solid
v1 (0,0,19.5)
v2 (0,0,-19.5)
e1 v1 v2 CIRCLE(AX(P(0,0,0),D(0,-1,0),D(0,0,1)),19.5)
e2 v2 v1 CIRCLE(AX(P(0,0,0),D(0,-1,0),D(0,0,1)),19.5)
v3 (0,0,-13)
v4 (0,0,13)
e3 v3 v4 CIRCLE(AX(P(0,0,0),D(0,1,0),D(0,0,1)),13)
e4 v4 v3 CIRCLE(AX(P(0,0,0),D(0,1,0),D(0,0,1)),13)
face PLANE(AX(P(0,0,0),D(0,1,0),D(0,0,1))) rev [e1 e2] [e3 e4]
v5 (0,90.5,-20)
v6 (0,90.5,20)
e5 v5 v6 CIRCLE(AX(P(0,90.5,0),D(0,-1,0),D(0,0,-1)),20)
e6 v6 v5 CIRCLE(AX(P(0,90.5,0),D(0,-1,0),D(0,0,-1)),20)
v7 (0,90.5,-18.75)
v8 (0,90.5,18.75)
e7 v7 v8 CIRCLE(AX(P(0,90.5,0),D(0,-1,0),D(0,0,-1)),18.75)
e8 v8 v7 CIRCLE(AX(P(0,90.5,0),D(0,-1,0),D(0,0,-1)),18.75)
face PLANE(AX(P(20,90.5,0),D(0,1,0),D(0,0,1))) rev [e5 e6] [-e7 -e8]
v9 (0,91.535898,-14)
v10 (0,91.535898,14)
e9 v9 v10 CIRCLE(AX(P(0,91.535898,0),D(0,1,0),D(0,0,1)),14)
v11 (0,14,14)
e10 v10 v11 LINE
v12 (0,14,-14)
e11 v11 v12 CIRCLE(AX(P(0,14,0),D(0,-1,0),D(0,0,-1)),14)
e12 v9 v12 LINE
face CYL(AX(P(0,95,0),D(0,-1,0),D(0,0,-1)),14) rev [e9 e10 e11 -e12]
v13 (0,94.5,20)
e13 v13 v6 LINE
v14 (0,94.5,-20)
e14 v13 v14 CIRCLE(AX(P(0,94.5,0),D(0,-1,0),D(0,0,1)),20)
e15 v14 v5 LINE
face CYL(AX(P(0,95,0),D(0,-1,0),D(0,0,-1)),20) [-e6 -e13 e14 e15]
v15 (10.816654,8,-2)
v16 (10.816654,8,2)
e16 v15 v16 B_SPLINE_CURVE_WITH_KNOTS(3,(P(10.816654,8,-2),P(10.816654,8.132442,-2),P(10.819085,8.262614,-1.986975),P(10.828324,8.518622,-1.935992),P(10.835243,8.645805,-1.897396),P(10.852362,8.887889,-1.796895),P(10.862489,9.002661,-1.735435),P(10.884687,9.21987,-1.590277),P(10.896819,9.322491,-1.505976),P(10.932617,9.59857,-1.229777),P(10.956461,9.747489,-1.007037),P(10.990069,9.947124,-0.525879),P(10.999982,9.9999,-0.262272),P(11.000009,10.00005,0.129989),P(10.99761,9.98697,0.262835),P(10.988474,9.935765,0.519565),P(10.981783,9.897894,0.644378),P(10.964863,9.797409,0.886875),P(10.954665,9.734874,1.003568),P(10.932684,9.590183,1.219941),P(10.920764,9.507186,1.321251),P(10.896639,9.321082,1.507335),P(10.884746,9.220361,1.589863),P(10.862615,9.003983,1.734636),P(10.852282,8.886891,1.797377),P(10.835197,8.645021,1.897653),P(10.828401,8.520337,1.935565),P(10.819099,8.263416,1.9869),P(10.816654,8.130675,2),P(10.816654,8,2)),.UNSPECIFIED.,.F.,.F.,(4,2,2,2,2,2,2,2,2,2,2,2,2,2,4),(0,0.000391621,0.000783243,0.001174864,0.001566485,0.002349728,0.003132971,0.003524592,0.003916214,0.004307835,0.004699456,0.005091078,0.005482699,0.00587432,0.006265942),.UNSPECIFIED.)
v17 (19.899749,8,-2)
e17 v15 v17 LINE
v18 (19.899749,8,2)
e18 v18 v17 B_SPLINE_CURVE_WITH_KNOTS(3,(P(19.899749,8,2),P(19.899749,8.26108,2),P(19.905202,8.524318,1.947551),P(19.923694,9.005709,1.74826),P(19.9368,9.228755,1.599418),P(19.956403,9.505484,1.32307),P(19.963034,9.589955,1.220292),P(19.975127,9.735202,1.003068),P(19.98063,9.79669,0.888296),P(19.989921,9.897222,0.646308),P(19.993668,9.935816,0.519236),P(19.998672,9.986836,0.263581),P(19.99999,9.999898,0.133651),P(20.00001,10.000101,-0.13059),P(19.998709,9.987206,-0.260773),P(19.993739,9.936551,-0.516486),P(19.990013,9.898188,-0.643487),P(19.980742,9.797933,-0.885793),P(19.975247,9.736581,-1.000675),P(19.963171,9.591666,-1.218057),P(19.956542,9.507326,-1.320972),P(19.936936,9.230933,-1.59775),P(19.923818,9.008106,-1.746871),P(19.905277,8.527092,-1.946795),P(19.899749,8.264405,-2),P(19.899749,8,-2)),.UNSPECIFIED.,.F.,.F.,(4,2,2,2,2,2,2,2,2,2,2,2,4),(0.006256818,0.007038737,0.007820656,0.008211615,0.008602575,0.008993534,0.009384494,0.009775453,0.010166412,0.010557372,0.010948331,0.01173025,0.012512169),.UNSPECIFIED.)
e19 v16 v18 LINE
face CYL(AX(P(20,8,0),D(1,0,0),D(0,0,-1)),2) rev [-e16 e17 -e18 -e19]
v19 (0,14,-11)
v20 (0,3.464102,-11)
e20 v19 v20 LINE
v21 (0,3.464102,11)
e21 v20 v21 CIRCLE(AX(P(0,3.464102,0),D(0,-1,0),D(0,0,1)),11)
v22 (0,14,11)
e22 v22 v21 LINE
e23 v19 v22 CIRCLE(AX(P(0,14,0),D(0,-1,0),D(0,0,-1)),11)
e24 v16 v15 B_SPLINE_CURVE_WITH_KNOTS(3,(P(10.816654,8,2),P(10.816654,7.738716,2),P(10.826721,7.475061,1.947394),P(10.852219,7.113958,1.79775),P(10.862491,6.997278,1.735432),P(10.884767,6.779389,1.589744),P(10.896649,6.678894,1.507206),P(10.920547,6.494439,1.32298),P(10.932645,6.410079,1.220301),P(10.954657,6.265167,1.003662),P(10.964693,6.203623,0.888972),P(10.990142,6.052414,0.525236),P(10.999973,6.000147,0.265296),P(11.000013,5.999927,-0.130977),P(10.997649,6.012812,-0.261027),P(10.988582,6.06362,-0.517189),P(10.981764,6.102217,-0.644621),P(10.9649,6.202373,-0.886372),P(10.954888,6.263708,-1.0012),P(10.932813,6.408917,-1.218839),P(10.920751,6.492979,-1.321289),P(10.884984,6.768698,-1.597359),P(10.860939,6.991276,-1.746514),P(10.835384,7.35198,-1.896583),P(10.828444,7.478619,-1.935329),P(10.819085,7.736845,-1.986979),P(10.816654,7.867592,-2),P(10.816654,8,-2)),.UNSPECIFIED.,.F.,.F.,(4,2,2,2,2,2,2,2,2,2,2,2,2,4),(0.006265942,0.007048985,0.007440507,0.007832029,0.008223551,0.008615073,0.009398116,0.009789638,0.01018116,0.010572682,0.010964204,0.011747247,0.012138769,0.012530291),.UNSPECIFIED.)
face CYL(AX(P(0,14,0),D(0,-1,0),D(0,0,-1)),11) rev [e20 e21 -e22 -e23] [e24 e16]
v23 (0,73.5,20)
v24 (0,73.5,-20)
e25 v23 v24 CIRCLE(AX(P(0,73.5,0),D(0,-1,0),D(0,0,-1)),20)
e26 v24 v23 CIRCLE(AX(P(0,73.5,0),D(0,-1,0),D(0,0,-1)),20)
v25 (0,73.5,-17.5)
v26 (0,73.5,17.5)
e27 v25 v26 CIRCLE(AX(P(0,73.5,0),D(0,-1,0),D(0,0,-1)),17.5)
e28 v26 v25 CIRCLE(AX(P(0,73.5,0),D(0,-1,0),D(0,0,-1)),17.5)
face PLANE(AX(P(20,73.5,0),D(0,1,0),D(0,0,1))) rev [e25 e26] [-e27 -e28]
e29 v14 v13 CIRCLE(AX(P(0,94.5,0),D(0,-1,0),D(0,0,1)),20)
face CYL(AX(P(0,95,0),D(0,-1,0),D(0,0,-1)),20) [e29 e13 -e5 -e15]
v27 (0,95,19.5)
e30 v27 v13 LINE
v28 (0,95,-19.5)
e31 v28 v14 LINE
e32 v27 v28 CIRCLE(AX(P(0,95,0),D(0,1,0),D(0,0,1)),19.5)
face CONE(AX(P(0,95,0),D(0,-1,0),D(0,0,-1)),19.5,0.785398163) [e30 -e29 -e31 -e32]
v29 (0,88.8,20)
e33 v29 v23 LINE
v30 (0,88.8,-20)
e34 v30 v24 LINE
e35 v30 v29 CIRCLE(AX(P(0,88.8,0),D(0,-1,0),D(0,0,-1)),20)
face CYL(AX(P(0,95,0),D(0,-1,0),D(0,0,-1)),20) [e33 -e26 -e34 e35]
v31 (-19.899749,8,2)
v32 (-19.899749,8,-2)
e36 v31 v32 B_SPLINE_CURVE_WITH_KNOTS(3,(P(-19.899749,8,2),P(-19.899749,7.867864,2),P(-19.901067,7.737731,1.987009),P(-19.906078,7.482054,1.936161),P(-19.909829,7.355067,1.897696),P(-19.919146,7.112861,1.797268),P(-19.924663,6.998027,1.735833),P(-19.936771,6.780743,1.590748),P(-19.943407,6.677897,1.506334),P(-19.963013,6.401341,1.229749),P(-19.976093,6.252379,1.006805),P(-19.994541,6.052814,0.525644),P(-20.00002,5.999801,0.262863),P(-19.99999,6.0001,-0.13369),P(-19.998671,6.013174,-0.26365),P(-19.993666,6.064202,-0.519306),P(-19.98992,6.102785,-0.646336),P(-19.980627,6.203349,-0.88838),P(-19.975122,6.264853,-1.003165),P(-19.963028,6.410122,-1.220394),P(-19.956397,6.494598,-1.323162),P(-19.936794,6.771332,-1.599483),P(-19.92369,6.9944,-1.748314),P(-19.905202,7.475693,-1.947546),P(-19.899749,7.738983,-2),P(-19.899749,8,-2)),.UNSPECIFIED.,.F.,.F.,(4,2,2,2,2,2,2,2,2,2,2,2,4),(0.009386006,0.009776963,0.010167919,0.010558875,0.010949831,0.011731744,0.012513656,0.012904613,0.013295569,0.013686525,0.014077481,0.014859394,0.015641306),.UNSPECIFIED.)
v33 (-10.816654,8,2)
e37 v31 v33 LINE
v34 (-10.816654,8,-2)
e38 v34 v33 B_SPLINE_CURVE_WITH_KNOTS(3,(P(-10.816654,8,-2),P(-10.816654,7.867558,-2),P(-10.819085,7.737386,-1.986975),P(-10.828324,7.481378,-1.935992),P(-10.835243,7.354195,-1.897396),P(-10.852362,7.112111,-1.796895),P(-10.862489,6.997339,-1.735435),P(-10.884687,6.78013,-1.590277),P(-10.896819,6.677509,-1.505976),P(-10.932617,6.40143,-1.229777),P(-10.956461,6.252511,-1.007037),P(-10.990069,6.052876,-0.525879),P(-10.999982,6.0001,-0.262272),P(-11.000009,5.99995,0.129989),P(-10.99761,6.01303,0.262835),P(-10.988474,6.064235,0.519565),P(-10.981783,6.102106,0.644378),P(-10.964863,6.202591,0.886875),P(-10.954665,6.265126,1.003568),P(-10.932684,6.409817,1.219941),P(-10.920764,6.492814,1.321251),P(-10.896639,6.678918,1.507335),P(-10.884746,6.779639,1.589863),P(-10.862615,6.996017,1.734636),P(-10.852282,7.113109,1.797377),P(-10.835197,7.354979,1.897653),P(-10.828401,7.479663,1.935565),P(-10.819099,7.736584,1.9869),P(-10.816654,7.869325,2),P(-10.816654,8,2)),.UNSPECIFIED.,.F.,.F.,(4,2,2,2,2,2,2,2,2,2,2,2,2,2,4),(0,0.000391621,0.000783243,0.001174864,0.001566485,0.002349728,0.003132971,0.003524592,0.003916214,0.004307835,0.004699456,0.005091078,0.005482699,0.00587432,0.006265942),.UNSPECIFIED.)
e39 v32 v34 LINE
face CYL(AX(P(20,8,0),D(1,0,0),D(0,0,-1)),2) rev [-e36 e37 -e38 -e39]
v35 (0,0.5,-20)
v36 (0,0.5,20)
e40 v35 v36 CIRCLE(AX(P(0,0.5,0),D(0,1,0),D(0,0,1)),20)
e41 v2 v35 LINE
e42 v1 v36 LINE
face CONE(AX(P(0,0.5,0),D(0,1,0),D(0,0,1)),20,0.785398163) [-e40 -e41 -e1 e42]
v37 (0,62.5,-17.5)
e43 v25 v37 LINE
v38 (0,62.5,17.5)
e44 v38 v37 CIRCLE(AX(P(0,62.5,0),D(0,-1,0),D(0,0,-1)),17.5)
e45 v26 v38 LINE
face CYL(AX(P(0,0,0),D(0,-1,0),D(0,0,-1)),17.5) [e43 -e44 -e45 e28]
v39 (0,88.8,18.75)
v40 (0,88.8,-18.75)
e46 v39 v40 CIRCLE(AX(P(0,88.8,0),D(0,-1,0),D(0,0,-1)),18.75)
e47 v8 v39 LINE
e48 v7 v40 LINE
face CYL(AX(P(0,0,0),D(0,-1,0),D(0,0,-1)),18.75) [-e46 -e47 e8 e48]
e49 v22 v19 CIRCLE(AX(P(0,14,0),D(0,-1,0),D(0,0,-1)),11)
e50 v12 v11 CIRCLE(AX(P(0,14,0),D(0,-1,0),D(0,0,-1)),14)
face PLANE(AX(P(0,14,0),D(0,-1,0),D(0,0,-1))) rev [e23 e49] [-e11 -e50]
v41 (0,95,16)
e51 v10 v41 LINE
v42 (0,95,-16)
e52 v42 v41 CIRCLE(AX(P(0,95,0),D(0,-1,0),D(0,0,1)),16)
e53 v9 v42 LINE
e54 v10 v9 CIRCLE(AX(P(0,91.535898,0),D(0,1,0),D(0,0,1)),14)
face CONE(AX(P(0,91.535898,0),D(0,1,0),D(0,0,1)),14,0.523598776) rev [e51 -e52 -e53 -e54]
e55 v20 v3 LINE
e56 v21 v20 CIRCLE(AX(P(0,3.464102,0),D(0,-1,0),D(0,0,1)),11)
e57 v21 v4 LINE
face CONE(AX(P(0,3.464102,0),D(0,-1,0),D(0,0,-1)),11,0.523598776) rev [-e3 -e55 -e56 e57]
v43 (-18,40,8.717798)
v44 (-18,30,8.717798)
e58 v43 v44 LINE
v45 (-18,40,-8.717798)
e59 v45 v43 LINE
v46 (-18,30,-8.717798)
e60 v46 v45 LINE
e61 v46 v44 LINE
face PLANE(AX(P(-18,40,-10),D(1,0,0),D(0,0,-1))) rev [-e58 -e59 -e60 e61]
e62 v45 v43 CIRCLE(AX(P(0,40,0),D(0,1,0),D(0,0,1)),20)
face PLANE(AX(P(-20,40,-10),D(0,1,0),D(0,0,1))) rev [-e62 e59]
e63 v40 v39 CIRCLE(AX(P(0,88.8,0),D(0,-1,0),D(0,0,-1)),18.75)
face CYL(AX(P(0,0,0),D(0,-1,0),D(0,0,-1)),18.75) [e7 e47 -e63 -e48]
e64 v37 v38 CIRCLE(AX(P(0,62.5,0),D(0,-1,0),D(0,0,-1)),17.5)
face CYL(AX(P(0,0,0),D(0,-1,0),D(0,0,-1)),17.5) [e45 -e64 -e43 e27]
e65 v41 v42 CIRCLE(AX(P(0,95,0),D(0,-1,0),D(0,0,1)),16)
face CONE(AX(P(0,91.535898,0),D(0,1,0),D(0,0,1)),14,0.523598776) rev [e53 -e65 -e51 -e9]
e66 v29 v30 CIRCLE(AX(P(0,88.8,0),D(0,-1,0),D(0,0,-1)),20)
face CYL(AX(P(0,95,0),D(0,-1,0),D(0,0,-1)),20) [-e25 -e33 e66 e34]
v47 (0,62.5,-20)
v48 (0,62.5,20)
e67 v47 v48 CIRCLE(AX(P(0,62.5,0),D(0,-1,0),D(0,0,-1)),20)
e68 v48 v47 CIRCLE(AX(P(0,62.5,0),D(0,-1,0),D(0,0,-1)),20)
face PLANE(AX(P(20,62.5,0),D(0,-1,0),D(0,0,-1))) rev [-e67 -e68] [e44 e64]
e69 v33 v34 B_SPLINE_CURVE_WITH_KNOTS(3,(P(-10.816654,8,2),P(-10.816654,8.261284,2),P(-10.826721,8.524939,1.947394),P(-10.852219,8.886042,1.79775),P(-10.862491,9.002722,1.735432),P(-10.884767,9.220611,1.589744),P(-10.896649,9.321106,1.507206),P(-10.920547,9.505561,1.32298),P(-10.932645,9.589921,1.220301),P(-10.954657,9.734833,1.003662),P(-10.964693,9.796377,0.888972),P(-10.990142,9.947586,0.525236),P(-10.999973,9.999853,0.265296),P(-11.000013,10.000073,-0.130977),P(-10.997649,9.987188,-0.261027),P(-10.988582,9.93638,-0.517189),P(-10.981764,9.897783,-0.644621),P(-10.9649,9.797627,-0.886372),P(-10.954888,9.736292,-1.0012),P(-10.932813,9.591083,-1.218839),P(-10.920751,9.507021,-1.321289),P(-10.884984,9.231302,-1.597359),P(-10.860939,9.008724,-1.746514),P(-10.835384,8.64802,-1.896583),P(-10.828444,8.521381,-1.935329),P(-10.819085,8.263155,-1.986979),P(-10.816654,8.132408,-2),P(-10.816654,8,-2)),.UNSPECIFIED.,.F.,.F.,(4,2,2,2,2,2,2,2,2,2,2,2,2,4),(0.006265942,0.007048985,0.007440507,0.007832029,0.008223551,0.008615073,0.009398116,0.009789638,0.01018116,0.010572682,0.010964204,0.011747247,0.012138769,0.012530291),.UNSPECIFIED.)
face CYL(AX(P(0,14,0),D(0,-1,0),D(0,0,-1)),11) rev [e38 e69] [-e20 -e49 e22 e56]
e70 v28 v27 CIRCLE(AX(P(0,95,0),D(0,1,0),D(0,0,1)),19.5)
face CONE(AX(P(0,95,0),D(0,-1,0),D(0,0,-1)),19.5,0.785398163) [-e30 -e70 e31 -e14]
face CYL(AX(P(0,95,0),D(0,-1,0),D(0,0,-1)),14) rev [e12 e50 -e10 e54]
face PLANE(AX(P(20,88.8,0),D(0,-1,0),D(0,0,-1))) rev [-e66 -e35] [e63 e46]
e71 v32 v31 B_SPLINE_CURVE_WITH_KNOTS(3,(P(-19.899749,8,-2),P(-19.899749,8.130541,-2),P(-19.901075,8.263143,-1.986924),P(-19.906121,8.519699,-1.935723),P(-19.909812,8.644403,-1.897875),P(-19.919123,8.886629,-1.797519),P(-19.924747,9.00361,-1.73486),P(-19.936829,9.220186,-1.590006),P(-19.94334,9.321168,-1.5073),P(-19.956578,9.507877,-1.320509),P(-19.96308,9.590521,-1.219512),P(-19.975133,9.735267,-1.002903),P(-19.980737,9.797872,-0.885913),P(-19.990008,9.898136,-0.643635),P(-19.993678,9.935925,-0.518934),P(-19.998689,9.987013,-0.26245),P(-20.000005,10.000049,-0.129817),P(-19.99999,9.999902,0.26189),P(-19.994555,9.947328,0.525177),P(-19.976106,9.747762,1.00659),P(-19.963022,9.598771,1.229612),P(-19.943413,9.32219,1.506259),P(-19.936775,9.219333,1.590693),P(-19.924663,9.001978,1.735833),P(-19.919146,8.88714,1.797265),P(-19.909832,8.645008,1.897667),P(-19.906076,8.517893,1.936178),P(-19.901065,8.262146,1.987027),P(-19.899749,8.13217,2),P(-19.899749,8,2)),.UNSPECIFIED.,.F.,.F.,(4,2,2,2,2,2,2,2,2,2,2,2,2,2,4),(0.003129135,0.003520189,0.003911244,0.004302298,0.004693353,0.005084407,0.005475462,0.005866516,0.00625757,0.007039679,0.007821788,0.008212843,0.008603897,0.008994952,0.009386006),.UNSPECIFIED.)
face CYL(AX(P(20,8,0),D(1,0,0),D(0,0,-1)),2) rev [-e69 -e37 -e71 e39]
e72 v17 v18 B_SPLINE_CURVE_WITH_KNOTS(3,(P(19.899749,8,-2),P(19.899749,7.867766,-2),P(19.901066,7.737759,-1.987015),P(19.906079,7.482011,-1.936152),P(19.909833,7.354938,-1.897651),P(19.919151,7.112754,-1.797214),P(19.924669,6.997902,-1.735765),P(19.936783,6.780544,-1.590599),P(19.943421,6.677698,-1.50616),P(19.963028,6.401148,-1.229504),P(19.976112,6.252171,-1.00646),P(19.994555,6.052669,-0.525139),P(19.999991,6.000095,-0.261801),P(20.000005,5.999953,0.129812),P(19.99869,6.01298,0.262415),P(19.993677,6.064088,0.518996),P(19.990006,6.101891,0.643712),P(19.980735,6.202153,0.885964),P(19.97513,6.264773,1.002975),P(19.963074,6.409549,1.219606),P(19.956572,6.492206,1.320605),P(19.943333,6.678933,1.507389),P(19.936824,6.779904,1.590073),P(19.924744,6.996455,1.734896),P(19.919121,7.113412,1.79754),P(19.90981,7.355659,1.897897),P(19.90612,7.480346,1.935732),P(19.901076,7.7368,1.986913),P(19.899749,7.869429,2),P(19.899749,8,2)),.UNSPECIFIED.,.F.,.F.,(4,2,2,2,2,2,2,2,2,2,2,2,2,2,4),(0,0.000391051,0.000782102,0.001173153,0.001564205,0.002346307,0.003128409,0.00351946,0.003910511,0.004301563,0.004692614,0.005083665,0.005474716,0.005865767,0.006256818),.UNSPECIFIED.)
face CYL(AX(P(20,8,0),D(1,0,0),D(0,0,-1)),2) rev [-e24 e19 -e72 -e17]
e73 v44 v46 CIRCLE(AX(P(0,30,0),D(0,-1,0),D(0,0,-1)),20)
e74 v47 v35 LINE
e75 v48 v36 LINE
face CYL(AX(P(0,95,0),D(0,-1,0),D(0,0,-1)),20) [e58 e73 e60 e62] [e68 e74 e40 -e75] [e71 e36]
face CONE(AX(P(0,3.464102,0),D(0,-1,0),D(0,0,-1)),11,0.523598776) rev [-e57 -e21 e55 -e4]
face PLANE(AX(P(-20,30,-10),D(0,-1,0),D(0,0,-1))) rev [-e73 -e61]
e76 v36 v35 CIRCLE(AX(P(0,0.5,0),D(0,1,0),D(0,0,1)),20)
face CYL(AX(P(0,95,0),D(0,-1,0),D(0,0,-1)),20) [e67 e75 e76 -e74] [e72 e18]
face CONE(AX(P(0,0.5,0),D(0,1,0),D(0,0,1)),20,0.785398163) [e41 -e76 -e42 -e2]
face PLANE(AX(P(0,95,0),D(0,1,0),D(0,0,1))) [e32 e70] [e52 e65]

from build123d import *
from OCP.BRepFilletAPI import BRepFilletAPI_MakeChamfer

# Parameters (mm, degrees)
SKETCH_1_R            = 20
SKETCH_1_R_2          = 14
EXTRUDE_1_DEPTH       = 95
SKETCH_3_W            = 2.5
SKETCH_3_H            = 11
SKETCH_3_W_2          = 1.25
SKETCH_3_H_2          = 1.7
SKETCH_4_R            = 14
SKETCH_4_R_2          = 11
EXTRUDE_2_DEPTH       = 14
CHAMFER_1_SIZE        = 0.5
HOLE_WIZARD_4_0_4_3_D = 4
SKETCH_7_W            = 2
SKETCH_7_H            = 10
CUT_EXTRUDE_1_DEPTH   = 10
CHAMFER_2_SIZE        = 2
CHAMFER_2_SIZE2       = 3.464101615


with BuildPart() as part:
    # 草图1 → 凸台-拉伸1 (new body)
    with BuildSketch(Plane(origin=(0, 0, 0), x_dir=(1, 0, 0), z_dir=(0, 1, 0))):
        with Locations(Location((0, 0, 0), (0, 0, 270))):
            Circle(SKETCH_1_R)
        with Locations(Location((0, 0, 0), (0, 0, 270))):
            Circle(SKETCH_1_R_2, mode=Mode.SUBTRACT)
    extrude(amount=EXTRUDE_1_DEPTH)

    # 草图3 → 切除-旋转1 (revolve, cut)
    with BuildSketch(Plane.XY, mode=Mode.PRIVATE) as cut_revolve_1_sk:
        with Locations((18.75, 68)):
            Rectangle(SKETCH_3_W, SKETCH_3_H)
        with Locations((19.375, 89.65)):
            Rectangle(SKETCH_3_W_2, SKETCH_3_H_2)
    revolve(cut_revolve_1_sk.sketch.rotate(Axis((0, 0, 0), (0, 1, 0)), 90), axis=Axis((0, 0, 0), (0, 1, 0)), mode=Mode.SUBTRACT)

    # 草图4 → 凸台-拉伸2 (add)
    with BuildSketch(Plane.XZ):
        with Locations(Location((0, 0, 0), (0, 0, 270))):
            Circle(SKETCH_4_R)
        with Locations(Location((0, 0, 0), (0, 0, 270))):
            Circle(SKETCH_4_R_2, mode=Mode.SUBTRACT)
    extrude(amount=-EXTRUDE_2_DEPTH)

    # 倒角1
    chamfer_1_edges = [part.edges().sort_by_distance(p)[0] for p in [
        (0, 0, -20),
        (0, 95, -20),
    ]]
    chamfer(chamfer_1_edges, length=CHAMFER_1_SIZE)

    # Ø4.0 (4) 直径孔3 (through all)
    with Locations(Plane(origin=(20, 8, 0), x_dir=(0, 0, 1), z_dir=(1, 0, 0))):
        with Locations((0, 0)):
            Hole(HOLE_WIZARD_4_0_4_3_D / 2)

    # 草图7 → 切除-拉伸1 (cut, symmetric)
    with BuildSketch(Plane.XY):
        with Locations((-19, 35)):
            Rectangle(SKETCH_7_W, SKETCH_7_H)
    extrude(amount=CUT_EXTRUDE_1_DEPTH, both=True, mode=Mode.SUBTRACT)

    # 倒角2: one chamfer whose edges measure the first distance from different faces: ONE call of the kernel's chamfer builder (chamfer() names one face for all edges)
    chamfer_2_edges_1 = [part.edges().sort_by_distance(p)[0] for p in [
        (0, 0, 11),
    ]]
    chamfer_2_side_1 = [part.faces().sort_by_distance(p)[0] for p in [
        (0, 0, -18.948456711),
    ]]
    chamfer_2_edges_2 = [part.edges().sort_by_distance(p)[0] for p in [
        (0, 95, -14),
    ]]
    chamfer_2_side_2 = [part.faces().sort_by_distance(p)[0] for p in [
        (0, 95, -18.948456711),
    ]]
    chamfer_2 = BRepFilletAPI_MakeChamfer(part.part.solid().wrapped)
    for e in chamfer_2_edges_1:
        chamfer_2.Add(CHAMFER_2_SIZE, CHAMFER_2_SIZE2, e.wrapped, chamfer_2_side_1[0].wrapped)  # the first distance lies on this face
    for e in chamfer_2_edges_2:
        chamfer_2.Add(CHAMFER_2_SIZE, CHAMFER_2_SIZE2, e.wrapped, chamfer_2_side_2[0].wrapped)  # the first distance lies on this face
    add(Compound.cast(chamfer_2.Shape()), mode=Mode.REPLACE)


solid = part.part
